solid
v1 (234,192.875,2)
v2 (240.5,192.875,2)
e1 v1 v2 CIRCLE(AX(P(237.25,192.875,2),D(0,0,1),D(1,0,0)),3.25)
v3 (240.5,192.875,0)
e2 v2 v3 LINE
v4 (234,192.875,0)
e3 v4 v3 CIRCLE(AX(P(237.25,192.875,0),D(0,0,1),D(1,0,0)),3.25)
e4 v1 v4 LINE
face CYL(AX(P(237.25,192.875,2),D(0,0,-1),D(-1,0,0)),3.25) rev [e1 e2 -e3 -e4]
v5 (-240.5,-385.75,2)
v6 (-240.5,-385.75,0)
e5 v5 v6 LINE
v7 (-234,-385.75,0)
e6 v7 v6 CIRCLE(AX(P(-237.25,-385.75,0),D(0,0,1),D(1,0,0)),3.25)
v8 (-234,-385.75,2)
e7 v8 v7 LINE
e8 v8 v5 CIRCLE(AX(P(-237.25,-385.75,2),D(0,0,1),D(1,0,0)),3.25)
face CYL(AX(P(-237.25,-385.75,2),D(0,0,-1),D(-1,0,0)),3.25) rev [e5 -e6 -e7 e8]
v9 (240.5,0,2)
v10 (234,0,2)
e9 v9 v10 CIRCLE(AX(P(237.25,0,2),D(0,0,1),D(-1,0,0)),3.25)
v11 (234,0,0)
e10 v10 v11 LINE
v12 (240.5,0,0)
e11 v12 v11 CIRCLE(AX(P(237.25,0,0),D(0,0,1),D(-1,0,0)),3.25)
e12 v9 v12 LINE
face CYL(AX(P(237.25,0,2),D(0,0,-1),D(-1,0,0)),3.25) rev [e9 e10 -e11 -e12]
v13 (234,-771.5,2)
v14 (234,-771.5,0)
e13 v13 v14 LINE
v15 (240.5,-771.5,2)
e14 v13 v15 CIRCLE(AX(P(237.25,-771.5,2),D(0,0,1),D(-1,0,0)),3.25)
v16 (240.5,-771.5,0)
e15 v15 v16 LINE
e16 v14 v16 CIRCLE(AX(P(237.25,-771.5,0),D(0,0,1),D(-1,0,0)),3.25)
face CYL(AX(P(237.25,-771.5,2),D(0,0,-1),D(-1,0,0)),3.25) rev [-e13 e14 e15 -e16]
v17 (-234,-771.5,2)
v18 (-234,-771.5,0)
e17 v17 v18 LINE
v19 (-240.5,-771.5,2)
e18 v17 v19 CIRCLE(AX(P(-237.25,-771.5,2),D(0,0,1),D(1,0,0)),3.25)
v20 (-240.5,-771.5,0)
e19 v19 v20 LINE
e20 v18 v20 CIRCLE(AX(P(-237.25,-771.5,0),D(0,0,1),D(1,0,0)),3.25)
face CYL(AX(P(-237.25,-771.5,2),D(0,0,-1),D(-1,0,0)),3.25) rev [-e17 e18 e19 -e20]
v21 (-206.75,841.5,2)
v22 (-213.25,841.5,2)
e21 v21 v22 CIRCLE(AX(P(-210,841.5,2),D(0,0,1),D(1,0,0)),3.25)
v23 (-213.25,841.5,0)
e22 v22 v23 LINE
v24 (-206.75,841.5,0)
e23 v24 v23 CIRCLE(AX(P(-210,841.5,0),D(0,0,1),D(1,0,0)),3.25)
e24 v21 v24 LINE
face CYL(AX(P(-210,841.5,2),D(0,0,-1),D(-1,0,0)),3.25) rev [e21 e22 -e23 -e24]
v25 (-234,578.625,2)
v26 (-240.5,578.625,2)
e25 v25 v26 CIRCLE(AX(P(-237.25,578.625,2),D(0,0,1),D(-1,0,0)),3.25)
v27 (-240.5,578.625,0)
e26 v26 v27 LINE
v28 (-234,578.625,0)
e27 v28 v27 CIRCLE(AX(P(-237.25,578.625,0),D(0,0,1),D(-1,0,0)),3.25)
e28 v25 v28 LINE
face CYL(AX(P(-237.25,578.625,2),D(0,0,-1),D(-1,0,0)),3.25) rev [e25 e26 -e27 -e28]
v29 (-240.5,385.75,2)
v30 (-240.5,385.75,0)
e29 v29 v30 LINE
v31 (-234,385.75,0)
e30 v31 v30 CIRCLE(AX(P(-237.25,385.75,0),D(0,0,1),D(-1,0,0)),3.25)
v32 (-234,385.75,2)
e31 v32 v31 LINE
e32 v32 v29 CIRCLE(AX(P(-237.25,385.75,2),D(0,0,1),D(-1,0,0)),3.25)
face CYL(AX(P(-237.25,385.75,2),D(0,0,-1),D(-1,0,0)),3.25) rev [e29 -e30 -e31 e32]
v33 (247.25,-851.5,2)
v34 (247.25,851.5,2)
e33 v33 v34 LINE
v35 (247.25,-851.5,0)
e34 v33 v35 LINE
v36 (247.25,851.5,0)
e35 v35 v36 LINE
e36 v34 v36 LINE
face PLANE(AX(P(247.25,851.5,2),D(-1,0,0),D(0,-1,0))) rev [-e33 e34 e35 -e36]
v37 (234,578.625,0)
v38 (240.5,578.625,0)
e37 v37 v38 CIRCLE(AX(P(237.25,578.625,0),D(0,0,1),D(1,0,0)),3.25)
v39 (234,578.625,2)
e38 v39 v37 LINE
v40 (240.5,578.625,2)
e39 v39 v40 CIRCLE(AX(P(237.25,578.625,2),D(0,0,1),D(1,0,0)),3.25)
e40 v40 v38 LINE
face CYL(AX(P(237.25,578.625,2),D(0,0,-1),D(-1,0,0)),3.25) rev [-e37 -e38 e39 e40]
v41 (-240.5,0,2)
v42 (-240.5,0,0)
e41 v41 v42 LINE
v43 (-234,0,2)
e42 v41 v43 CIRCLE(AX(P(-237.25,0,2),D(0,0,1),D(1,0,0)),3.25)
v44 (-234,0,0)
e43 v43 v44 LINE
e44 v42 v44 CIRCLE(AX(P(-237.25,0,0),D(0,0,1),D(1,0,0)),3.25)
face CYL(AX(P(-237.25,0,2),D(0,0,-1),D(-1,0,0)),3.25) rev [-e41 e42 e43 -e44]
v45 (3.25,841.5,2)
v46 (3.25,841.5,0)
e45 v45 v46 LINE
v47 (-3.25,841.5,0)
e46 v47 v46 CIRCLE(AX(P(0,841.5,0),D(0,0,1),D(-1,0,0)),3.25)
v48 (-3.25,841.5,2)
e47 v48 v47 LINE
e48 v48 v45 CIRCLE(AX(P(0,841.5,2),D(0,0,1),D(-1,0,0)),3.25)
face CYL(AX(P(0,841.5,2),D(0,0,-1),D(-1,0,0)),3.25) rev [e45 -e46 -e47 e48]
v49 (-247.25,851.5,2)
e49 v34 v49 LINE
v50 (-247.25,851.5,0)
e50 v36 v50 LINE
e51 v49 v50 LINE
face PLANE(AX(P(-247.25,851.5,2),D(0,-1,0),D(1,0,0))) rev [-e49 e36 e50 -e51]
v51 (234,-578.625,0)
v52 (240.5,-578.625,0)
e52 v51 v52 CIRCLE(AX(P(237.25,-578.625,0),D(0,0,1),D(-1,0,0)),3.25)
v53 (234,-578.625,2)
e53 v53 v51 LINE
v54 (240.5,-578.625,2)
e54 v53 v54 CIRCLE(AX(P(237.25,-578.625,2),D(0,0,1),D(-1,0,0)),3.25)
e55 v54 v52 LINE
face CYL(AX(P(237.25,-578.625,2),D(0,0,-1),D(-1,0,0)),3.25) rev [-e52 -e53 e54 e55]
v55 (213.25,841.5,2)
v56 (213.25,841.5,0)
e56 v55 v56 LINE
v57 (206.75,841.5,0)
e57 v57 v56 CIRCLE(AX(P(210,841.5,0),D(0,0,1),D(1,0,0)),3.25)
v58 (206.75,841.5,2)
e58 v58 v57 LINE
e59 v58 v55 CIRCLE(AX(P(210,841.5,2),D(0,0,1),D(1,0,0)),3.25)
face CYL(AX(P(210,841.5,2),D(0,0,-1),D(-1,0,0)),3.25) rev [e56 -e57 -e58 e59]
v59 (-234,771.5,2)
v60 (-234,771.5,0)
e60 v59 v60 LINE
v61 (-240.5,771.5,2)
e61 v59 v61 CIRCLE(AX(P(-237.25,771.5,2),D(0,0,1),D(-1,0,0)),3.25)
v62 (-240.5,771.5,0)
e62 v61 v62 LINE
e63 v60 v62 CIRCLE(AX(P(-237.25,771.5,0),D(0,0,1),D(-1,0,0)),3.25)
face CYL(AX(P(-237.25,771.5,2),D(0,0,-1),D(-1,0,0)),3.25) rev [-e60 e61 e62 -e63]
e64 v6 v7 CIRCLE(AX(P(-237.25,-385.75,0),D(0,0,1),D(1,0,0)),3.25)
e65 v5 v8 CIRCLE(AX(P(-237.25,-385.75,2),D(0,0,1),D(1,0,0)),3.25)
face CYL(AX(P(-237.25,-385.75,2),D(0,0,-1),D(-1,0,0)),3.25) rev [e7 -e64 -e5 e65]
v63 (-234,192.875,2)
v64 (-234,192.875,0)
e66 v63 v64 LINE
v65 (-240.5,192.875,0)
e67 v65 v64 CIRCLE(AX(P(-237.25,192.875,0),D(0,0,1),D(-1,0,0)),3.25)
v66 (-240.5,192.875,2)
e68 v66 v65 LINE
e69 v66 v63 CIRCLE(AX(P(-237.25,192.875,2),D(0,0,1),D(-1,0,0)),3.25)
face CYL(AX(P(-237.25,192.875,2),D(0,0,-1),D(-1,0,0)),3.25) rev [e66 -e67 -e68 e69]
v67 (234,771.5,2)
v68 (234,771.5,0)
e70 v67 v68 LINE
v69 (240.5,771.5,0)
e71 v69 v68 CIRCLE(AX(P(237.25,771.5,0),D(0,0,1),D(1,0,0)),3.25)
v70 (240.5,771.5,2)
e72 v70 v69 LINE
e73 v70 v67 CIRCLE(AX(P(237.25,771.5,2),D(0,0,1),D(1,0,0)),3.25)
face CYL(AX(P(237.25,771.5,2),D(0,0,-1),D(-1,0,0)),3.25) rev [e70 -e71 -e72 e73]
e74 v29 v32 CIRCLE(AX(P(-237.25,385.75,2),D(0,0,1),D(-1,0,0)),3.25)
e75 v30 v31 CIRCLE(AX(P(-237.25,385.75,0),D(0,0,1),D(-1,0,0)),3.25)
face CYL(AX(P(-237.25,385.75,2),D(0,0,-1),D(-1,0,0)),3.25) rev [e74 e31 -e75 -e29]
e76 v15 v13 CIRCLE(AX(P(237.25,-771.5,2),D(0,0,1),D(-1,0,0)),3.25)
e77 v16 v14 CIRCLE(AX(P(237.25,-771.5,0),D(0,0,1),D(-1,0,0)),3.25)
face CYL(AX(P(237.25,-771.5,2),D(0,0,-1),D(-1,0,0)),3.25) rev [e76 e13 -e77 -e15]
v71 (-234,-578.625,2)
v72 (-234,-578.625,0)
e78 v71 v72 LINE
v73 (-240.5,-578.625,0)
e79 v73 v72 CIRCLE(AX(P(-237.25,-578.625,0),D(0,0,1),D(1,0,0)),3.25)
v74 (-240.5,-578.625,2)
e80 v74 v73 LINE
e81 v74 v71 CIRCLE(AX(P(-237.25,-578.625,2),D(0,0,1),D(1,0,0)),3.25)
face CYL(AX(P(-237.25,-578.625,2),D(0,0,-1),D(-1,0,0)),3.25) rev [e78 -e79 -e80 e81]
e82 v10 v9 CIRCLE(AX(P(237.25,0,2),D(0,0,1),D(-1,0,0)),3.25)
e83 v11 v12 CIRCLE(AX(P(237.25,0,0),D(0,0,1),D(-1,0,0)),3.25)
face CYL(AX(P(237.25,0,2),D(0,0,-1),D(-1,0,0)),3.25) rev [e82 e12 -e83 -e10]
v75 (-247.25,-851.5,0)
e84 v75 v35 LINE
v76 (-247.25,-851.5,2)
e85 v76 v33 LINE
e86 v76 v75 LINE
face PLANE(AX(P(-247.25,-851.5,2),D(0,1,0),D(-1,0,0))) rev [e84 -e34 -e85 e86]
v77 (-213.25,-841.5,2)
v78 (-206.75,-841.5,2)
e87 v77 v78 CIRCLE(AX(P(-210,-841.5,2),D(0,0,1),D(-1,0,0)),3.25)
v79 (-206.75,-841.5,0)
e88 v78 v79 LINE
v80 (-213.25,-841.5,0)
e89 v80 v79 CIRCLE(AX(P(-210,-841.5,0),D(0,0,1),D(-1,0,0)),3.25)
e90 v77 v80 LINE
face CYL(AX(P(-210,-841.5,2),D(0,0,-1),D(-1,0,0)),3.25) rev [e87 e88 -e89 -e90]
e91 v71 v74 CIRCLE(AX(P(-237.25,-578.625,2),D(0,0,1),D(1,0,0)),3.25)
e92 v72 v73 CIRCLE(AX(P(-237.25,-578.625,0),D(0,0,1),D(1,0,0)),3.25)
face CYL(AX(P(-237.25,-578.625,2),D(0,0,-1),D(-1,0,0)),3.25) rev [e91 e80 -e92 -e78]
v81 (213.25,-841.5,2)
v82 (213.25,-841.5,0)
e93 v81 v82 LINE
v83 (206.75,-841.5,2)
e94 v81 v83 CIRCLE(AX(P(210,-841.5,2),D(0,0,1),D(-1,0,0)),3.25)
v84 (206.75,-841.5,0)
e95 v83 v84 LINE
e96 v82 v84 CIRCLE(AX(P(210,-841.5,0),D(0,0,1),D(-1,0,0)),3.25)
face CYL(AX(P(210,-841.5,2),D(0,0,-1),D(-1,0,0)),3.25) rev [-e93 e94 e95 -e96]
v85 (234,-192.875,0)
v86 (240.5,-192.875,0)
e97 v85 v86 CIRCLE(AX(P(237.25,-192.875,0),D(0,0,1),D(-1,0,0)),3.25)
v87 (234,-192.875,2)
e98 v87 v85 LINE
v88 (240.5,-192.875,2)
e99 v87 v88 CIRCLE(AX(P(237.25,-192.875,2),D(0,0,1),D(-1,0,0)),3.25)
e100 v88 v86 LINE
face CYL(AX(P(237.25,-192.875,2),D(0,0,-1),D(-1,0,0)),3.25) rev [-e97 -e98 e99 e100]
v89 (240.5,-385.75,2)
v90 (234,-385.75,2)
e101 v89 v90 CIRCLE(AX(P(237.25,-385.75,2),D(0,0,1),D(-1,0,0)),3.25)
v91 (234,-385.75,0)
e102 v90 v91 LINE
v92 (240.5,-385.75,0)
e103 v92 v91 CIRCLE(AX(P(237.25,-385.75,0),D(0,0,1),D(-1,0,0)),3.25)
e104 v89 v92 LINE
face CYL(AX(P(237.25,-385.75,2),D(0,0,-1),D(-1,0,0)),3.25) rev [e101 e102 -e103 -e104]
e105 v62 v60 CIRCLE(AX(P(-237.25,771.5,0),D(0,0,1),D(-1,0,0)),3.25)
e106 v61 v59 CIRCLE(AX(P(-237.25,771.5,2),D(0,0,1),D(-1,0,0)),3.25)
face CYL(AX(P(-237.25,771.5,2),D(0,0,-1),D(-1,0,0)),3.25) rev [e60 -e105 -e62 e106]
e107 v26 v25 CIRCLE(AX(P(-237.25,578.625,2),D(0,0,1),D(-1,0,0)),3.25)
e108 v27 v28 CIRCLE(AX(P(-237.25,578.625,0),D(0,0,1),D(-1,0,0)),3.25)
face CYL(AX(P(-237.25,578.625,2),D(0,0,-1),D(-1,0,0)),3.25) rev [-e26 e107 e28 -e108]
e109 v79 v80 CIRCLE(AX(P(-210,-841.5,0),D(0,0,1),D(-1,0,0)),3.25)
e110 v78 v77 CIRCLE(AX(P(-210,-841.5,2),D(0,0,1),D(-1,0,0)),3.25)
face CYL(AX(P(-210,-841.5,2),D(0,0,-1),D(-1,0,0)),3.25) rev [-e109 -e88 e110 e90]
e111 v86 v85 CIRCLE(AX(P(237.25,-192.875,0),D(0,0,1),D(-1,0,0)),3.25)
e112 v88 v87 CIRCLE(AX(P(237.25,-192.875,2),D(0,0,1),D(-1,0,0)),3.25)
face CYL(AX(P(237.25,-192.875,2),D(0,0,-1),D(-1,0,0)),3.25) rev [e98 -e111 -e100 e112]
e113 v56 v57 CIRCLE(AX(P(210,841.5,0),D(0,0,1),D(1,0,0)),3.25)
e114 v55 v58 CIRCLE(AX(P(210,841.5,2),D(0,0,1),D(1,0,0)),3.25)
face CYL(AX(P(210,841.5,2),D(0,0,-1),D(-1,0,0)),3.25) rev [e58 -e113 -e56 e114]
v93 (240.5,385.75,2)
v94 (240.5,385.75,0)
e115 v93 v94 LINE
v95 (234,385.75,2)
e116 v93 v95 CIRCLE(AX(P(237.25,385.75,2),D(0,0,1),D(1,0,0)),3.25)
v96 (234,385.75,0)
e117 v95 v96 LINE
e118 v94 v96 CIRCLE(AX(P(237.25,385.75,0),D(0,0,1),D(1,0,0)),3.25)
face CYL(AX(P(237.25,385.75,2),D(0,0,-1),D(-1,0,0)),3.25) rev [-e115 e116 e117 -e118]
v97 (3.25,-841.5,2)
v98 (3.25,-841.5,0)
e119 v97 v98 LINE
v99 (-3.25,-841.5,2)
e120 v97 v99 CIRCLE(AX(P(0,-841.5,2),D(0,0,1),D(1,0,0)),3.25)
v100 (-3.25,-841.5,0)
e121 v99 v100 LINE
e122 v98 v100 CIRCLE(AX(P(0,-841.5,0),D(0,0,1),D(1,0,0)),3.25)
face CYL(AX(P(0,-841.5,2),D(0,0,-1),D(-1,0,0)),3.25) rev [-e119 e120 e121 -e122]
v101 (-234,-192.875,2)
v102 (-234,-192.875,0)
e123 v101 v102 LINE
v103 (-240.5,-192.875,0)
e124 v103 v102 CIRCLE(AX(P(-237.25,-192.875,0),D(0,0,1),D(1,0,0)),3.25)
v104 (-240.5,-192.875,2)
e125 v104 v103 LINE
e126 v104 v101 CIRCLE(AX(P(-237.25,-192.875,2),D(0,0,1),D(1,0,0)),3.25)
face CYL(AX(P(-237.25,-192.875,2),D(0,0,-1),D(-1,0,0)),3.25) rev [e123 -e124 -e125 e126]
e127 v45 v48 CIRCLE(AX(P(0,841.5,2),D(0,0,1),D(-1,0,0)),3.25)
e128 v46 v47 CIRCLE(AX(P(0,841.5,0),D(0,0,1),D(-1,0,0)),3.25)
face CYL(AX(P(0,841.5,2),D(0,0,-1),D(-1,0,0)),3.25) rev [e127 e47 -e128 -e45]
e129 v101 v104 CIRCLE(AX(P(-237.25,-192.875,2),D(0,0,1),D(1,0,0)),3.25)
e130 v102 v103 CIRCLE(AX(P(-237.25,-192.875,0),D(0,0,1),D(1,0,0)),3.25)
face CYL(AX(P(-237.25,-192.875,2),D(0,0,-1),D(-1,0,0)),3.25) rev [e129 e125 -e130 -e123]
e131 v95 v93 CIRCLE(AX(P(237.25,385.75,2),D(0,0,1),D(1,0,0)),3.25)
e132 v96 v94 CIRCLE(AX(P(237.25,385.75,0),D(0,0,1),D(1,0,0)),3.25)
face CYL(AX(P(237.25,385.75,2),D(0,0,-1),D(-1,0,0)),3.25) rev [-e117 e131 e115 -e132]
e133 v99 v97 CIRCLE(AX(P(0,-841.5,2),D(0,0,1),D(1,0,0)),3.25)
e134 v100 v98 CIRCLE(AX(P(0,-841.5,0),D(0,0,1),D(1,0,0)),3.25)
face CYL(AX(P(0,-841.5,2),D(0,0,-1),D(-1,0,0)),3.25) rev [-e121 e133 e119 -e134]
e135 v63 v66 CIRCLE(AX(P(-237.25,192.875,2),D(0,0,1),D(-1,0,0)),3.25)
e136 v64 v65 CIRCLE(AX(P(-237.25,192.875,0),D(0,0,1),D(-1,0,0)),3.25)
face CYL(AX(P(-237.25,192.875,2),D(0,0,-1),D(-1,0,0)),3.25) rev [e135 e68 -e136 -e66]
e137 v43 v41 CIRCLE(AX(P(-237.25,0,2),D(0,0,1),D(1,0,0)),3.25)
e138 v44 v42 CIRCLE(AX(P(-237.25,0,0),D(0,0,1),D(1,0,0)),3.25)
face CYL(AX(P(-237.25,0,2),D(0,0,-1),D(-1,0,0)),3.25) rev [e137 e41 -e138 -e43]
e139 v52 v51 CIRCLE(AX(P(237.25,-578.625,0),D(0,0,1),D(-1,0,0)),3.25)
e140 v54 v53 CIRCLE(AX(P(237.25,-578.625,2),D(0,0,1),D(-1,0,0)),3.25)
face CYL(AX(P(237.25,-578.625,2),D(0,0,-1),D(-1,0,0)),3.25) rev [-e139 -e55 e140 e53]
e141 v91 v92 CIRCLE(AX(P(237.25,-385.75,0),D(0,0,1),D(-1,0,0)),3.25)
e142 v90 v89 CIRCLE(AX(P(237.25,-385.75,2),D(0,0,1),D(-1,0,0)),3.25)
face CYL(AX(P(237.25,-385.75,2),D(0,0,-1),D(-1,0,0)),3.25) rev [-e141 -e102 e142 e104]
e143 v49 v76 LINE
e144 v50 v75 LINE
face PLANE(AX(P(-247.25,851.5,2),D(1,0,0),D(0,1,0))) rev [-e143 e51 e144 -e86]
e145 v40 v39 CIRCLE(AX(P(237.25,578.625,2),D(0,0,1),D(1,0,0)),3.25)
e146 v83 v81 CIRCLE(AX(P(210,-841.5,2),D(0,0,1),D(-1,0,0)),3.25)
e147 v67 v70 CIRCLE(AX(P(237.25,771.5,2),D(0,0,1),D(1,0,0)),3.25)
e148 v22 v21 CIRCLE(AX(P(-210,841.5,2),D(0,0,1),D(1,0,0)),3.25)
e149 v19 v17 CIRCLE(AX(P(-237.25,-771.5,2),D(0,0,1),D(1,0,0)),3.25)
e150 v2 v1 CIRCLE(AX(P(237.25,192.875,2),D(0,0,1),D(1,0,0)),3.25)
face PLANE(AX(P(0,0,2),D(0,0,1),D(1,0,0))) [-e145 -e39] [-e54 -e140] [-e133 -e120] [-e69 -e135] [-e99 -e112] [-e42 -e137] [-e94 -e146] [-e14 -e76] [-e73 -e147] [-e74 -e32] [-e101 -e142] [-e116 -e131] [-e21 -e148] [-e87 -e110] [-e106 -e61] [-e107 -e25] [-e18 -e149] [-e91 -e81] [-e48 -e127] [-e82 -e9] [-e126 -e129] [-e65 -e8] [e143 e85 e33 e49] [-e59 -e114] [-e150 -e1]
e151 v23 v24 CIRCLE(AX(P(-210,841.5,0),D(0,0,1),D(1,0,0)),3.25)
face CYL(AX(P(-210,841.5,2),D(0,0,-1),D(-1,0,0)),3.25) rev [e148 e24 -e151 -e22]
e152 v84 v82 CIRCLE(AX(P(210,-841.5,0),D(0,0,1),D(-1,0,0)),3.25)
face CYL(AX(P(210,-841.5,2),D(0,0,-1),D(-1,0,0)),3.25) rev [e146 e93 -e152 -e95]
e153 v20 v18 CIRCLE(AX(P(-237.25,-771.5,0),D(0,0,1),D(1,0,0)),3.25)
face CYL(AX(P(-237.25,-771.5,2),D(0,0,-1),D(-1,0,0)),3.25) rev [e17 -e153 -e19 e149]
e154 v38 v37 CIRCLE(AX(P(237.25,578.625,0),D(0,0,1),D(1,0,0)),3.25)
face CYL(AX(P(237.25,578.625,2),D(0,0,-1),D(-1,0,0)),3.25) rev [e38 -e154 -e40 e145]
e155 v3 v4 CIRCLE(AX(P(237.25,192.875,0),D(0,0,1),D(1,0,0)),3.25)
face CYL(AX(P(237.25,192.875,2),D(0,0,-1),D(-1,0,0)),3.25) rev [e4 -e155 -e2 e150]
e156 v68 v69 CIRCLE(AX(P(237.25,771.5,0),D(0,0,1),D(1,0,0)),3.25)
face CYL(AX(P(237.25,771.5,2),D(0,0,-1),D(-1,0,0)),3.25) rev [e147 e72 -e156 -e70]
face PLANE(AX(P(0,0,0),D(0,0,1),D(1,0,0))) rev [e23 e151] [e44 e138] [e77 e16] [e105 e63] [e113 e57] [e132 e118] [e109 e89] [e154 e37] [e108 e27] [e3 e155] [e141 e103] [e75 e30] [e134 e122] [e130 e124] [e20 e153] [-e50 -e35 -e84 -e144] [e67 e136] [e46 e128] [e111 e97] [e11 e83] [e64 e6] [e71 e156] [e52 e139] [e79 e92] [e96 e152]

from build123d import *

# Parameters (mm, degrees)
SKETCH_1_W      = 494.5
SKETCH_1_H      = 1703
SKETCH_1_R      = 3.25
EXTRUDE_1_DEPTH = 2


with BuildPart() as part:
    # 草图1 → 凸台-拉伸1 (new body)
    with BuildSketch(Plane.XY):
        Rectangle(SKETCH_1_W, SKETCH_1_H)
        with Locations((-237.25, 0)):
            Circle(SKETCH_1_R, mode=Mode.SUBTRACT)
        with Locations((-237.25, -192.875)):
            Circle(SKETCH_1_R, mode=Mode.SUBTRACT)
        with Locations((-237.25, -385.75)):
            Circle(SKETCH_1_R, mode=Mode.SUBTRACT)
        with Locations((-237.25, -578.625)):
            Circle(SKETCH_1_R, mode=Mode.SUBTRACT)
        with Locations((-237.25, -771.5)):
            Circle(SKETCH_1_R, mode=Mode.SUBTRACT)
        with Locations((0, -841.5)):
            Circle(SKETCH_1_R, mode=Mode.SUBTRACT)
        with Locations(Location((0, 841.5, 0), (0, 0, 180))):
            Circle(SKETCH_1_R, mode=Mode.SUBTRACT)
        with Locations(Location((-237.25, 771.5, 0), (0, 0, 180))):
            Circle(SKETCH_1_R, mode=Mode.SUBTRACT)
        with Locations(Location((-237.25, 578.625, 0), (0, 0, 180))):
            Circle(SKETCH_1_R, mode=Mode.SUBTRACT)
        with Locations(Location((-237.25, 385.75, 0), (0, 0, 180))):
            Circle(SKETCH_1_R, mode=Mode.SUBTRACT)
        with Locations(Location((-237.25, 192.875, 0), (0, 0, 180))):
            Circle(SKETCH_1_R, mode=Mode.SUBTRACT)
        with Locations((237.25, 192.875)):
            Circle(SKETCH_1_R, mode=Mode.SUBTRACT)
        with Locations((237.25, 385.75)):
            Circle(SKETCH_1_R, mode=Mode.SUBTRACT)
        with Locations((237.25, 578.625)):
            Circle(SKETCH_1_R, mode=Mode.SUBTRACT)
        with Locations((237.25, 771.5)):
            Circle(SKETCH_1_R, mode=Mode.SUBTRACT)
        with Locations(Location((237.25, -771.5, 0), (0, 0, 180))):
            Circle(SKETCH_1_R, mode=Mode.SUBTRACT)
        with Locations(Location((237.25, -578.625, 0), (0, 0, 180))):
            Circle(SKETCH_1_R, mode=Mode.SUBTRACT)
        with Locations(Location((237.25, -385.75, 0), (0, 0, 180))):
            Circle(SKETCH_1_R, mode=Mode.SUBTRACT)
        with Locations(Location((237.25, -192.875, 0), (0, 0, 180))):
            Circle(SKETCH_1_R, mode=Mode.SUBTRACT)
        with Locations(Location((237.25, 0, 0), (0, 0, 180))):
            Circle(SKETCH_1_R, mode=Mode.SUBTRACT)
        with Locations((-210, 841.5)):
            Circle(SKETCH_1_R, mode=Mode.SUBTRACT)
        with Locations((210, 841.5)):
            Circle(SKETCH_1_R, mode=Mode.SUBTRACT)
        with Locations(Location((-210, -841.5, 0), (0, 0, 180))):
            Circle(SKETCH_1_R, mode=Mode.SUBTRACT)
        with Locations(Location((210, -841.5, 0), (0, 0, 180))):
            Circle(SKETCH_1_R, mode=Mode.SUBTRACT)
    extrude(amount=EXTRUDE_1_DEPTH)


solid = part.part
